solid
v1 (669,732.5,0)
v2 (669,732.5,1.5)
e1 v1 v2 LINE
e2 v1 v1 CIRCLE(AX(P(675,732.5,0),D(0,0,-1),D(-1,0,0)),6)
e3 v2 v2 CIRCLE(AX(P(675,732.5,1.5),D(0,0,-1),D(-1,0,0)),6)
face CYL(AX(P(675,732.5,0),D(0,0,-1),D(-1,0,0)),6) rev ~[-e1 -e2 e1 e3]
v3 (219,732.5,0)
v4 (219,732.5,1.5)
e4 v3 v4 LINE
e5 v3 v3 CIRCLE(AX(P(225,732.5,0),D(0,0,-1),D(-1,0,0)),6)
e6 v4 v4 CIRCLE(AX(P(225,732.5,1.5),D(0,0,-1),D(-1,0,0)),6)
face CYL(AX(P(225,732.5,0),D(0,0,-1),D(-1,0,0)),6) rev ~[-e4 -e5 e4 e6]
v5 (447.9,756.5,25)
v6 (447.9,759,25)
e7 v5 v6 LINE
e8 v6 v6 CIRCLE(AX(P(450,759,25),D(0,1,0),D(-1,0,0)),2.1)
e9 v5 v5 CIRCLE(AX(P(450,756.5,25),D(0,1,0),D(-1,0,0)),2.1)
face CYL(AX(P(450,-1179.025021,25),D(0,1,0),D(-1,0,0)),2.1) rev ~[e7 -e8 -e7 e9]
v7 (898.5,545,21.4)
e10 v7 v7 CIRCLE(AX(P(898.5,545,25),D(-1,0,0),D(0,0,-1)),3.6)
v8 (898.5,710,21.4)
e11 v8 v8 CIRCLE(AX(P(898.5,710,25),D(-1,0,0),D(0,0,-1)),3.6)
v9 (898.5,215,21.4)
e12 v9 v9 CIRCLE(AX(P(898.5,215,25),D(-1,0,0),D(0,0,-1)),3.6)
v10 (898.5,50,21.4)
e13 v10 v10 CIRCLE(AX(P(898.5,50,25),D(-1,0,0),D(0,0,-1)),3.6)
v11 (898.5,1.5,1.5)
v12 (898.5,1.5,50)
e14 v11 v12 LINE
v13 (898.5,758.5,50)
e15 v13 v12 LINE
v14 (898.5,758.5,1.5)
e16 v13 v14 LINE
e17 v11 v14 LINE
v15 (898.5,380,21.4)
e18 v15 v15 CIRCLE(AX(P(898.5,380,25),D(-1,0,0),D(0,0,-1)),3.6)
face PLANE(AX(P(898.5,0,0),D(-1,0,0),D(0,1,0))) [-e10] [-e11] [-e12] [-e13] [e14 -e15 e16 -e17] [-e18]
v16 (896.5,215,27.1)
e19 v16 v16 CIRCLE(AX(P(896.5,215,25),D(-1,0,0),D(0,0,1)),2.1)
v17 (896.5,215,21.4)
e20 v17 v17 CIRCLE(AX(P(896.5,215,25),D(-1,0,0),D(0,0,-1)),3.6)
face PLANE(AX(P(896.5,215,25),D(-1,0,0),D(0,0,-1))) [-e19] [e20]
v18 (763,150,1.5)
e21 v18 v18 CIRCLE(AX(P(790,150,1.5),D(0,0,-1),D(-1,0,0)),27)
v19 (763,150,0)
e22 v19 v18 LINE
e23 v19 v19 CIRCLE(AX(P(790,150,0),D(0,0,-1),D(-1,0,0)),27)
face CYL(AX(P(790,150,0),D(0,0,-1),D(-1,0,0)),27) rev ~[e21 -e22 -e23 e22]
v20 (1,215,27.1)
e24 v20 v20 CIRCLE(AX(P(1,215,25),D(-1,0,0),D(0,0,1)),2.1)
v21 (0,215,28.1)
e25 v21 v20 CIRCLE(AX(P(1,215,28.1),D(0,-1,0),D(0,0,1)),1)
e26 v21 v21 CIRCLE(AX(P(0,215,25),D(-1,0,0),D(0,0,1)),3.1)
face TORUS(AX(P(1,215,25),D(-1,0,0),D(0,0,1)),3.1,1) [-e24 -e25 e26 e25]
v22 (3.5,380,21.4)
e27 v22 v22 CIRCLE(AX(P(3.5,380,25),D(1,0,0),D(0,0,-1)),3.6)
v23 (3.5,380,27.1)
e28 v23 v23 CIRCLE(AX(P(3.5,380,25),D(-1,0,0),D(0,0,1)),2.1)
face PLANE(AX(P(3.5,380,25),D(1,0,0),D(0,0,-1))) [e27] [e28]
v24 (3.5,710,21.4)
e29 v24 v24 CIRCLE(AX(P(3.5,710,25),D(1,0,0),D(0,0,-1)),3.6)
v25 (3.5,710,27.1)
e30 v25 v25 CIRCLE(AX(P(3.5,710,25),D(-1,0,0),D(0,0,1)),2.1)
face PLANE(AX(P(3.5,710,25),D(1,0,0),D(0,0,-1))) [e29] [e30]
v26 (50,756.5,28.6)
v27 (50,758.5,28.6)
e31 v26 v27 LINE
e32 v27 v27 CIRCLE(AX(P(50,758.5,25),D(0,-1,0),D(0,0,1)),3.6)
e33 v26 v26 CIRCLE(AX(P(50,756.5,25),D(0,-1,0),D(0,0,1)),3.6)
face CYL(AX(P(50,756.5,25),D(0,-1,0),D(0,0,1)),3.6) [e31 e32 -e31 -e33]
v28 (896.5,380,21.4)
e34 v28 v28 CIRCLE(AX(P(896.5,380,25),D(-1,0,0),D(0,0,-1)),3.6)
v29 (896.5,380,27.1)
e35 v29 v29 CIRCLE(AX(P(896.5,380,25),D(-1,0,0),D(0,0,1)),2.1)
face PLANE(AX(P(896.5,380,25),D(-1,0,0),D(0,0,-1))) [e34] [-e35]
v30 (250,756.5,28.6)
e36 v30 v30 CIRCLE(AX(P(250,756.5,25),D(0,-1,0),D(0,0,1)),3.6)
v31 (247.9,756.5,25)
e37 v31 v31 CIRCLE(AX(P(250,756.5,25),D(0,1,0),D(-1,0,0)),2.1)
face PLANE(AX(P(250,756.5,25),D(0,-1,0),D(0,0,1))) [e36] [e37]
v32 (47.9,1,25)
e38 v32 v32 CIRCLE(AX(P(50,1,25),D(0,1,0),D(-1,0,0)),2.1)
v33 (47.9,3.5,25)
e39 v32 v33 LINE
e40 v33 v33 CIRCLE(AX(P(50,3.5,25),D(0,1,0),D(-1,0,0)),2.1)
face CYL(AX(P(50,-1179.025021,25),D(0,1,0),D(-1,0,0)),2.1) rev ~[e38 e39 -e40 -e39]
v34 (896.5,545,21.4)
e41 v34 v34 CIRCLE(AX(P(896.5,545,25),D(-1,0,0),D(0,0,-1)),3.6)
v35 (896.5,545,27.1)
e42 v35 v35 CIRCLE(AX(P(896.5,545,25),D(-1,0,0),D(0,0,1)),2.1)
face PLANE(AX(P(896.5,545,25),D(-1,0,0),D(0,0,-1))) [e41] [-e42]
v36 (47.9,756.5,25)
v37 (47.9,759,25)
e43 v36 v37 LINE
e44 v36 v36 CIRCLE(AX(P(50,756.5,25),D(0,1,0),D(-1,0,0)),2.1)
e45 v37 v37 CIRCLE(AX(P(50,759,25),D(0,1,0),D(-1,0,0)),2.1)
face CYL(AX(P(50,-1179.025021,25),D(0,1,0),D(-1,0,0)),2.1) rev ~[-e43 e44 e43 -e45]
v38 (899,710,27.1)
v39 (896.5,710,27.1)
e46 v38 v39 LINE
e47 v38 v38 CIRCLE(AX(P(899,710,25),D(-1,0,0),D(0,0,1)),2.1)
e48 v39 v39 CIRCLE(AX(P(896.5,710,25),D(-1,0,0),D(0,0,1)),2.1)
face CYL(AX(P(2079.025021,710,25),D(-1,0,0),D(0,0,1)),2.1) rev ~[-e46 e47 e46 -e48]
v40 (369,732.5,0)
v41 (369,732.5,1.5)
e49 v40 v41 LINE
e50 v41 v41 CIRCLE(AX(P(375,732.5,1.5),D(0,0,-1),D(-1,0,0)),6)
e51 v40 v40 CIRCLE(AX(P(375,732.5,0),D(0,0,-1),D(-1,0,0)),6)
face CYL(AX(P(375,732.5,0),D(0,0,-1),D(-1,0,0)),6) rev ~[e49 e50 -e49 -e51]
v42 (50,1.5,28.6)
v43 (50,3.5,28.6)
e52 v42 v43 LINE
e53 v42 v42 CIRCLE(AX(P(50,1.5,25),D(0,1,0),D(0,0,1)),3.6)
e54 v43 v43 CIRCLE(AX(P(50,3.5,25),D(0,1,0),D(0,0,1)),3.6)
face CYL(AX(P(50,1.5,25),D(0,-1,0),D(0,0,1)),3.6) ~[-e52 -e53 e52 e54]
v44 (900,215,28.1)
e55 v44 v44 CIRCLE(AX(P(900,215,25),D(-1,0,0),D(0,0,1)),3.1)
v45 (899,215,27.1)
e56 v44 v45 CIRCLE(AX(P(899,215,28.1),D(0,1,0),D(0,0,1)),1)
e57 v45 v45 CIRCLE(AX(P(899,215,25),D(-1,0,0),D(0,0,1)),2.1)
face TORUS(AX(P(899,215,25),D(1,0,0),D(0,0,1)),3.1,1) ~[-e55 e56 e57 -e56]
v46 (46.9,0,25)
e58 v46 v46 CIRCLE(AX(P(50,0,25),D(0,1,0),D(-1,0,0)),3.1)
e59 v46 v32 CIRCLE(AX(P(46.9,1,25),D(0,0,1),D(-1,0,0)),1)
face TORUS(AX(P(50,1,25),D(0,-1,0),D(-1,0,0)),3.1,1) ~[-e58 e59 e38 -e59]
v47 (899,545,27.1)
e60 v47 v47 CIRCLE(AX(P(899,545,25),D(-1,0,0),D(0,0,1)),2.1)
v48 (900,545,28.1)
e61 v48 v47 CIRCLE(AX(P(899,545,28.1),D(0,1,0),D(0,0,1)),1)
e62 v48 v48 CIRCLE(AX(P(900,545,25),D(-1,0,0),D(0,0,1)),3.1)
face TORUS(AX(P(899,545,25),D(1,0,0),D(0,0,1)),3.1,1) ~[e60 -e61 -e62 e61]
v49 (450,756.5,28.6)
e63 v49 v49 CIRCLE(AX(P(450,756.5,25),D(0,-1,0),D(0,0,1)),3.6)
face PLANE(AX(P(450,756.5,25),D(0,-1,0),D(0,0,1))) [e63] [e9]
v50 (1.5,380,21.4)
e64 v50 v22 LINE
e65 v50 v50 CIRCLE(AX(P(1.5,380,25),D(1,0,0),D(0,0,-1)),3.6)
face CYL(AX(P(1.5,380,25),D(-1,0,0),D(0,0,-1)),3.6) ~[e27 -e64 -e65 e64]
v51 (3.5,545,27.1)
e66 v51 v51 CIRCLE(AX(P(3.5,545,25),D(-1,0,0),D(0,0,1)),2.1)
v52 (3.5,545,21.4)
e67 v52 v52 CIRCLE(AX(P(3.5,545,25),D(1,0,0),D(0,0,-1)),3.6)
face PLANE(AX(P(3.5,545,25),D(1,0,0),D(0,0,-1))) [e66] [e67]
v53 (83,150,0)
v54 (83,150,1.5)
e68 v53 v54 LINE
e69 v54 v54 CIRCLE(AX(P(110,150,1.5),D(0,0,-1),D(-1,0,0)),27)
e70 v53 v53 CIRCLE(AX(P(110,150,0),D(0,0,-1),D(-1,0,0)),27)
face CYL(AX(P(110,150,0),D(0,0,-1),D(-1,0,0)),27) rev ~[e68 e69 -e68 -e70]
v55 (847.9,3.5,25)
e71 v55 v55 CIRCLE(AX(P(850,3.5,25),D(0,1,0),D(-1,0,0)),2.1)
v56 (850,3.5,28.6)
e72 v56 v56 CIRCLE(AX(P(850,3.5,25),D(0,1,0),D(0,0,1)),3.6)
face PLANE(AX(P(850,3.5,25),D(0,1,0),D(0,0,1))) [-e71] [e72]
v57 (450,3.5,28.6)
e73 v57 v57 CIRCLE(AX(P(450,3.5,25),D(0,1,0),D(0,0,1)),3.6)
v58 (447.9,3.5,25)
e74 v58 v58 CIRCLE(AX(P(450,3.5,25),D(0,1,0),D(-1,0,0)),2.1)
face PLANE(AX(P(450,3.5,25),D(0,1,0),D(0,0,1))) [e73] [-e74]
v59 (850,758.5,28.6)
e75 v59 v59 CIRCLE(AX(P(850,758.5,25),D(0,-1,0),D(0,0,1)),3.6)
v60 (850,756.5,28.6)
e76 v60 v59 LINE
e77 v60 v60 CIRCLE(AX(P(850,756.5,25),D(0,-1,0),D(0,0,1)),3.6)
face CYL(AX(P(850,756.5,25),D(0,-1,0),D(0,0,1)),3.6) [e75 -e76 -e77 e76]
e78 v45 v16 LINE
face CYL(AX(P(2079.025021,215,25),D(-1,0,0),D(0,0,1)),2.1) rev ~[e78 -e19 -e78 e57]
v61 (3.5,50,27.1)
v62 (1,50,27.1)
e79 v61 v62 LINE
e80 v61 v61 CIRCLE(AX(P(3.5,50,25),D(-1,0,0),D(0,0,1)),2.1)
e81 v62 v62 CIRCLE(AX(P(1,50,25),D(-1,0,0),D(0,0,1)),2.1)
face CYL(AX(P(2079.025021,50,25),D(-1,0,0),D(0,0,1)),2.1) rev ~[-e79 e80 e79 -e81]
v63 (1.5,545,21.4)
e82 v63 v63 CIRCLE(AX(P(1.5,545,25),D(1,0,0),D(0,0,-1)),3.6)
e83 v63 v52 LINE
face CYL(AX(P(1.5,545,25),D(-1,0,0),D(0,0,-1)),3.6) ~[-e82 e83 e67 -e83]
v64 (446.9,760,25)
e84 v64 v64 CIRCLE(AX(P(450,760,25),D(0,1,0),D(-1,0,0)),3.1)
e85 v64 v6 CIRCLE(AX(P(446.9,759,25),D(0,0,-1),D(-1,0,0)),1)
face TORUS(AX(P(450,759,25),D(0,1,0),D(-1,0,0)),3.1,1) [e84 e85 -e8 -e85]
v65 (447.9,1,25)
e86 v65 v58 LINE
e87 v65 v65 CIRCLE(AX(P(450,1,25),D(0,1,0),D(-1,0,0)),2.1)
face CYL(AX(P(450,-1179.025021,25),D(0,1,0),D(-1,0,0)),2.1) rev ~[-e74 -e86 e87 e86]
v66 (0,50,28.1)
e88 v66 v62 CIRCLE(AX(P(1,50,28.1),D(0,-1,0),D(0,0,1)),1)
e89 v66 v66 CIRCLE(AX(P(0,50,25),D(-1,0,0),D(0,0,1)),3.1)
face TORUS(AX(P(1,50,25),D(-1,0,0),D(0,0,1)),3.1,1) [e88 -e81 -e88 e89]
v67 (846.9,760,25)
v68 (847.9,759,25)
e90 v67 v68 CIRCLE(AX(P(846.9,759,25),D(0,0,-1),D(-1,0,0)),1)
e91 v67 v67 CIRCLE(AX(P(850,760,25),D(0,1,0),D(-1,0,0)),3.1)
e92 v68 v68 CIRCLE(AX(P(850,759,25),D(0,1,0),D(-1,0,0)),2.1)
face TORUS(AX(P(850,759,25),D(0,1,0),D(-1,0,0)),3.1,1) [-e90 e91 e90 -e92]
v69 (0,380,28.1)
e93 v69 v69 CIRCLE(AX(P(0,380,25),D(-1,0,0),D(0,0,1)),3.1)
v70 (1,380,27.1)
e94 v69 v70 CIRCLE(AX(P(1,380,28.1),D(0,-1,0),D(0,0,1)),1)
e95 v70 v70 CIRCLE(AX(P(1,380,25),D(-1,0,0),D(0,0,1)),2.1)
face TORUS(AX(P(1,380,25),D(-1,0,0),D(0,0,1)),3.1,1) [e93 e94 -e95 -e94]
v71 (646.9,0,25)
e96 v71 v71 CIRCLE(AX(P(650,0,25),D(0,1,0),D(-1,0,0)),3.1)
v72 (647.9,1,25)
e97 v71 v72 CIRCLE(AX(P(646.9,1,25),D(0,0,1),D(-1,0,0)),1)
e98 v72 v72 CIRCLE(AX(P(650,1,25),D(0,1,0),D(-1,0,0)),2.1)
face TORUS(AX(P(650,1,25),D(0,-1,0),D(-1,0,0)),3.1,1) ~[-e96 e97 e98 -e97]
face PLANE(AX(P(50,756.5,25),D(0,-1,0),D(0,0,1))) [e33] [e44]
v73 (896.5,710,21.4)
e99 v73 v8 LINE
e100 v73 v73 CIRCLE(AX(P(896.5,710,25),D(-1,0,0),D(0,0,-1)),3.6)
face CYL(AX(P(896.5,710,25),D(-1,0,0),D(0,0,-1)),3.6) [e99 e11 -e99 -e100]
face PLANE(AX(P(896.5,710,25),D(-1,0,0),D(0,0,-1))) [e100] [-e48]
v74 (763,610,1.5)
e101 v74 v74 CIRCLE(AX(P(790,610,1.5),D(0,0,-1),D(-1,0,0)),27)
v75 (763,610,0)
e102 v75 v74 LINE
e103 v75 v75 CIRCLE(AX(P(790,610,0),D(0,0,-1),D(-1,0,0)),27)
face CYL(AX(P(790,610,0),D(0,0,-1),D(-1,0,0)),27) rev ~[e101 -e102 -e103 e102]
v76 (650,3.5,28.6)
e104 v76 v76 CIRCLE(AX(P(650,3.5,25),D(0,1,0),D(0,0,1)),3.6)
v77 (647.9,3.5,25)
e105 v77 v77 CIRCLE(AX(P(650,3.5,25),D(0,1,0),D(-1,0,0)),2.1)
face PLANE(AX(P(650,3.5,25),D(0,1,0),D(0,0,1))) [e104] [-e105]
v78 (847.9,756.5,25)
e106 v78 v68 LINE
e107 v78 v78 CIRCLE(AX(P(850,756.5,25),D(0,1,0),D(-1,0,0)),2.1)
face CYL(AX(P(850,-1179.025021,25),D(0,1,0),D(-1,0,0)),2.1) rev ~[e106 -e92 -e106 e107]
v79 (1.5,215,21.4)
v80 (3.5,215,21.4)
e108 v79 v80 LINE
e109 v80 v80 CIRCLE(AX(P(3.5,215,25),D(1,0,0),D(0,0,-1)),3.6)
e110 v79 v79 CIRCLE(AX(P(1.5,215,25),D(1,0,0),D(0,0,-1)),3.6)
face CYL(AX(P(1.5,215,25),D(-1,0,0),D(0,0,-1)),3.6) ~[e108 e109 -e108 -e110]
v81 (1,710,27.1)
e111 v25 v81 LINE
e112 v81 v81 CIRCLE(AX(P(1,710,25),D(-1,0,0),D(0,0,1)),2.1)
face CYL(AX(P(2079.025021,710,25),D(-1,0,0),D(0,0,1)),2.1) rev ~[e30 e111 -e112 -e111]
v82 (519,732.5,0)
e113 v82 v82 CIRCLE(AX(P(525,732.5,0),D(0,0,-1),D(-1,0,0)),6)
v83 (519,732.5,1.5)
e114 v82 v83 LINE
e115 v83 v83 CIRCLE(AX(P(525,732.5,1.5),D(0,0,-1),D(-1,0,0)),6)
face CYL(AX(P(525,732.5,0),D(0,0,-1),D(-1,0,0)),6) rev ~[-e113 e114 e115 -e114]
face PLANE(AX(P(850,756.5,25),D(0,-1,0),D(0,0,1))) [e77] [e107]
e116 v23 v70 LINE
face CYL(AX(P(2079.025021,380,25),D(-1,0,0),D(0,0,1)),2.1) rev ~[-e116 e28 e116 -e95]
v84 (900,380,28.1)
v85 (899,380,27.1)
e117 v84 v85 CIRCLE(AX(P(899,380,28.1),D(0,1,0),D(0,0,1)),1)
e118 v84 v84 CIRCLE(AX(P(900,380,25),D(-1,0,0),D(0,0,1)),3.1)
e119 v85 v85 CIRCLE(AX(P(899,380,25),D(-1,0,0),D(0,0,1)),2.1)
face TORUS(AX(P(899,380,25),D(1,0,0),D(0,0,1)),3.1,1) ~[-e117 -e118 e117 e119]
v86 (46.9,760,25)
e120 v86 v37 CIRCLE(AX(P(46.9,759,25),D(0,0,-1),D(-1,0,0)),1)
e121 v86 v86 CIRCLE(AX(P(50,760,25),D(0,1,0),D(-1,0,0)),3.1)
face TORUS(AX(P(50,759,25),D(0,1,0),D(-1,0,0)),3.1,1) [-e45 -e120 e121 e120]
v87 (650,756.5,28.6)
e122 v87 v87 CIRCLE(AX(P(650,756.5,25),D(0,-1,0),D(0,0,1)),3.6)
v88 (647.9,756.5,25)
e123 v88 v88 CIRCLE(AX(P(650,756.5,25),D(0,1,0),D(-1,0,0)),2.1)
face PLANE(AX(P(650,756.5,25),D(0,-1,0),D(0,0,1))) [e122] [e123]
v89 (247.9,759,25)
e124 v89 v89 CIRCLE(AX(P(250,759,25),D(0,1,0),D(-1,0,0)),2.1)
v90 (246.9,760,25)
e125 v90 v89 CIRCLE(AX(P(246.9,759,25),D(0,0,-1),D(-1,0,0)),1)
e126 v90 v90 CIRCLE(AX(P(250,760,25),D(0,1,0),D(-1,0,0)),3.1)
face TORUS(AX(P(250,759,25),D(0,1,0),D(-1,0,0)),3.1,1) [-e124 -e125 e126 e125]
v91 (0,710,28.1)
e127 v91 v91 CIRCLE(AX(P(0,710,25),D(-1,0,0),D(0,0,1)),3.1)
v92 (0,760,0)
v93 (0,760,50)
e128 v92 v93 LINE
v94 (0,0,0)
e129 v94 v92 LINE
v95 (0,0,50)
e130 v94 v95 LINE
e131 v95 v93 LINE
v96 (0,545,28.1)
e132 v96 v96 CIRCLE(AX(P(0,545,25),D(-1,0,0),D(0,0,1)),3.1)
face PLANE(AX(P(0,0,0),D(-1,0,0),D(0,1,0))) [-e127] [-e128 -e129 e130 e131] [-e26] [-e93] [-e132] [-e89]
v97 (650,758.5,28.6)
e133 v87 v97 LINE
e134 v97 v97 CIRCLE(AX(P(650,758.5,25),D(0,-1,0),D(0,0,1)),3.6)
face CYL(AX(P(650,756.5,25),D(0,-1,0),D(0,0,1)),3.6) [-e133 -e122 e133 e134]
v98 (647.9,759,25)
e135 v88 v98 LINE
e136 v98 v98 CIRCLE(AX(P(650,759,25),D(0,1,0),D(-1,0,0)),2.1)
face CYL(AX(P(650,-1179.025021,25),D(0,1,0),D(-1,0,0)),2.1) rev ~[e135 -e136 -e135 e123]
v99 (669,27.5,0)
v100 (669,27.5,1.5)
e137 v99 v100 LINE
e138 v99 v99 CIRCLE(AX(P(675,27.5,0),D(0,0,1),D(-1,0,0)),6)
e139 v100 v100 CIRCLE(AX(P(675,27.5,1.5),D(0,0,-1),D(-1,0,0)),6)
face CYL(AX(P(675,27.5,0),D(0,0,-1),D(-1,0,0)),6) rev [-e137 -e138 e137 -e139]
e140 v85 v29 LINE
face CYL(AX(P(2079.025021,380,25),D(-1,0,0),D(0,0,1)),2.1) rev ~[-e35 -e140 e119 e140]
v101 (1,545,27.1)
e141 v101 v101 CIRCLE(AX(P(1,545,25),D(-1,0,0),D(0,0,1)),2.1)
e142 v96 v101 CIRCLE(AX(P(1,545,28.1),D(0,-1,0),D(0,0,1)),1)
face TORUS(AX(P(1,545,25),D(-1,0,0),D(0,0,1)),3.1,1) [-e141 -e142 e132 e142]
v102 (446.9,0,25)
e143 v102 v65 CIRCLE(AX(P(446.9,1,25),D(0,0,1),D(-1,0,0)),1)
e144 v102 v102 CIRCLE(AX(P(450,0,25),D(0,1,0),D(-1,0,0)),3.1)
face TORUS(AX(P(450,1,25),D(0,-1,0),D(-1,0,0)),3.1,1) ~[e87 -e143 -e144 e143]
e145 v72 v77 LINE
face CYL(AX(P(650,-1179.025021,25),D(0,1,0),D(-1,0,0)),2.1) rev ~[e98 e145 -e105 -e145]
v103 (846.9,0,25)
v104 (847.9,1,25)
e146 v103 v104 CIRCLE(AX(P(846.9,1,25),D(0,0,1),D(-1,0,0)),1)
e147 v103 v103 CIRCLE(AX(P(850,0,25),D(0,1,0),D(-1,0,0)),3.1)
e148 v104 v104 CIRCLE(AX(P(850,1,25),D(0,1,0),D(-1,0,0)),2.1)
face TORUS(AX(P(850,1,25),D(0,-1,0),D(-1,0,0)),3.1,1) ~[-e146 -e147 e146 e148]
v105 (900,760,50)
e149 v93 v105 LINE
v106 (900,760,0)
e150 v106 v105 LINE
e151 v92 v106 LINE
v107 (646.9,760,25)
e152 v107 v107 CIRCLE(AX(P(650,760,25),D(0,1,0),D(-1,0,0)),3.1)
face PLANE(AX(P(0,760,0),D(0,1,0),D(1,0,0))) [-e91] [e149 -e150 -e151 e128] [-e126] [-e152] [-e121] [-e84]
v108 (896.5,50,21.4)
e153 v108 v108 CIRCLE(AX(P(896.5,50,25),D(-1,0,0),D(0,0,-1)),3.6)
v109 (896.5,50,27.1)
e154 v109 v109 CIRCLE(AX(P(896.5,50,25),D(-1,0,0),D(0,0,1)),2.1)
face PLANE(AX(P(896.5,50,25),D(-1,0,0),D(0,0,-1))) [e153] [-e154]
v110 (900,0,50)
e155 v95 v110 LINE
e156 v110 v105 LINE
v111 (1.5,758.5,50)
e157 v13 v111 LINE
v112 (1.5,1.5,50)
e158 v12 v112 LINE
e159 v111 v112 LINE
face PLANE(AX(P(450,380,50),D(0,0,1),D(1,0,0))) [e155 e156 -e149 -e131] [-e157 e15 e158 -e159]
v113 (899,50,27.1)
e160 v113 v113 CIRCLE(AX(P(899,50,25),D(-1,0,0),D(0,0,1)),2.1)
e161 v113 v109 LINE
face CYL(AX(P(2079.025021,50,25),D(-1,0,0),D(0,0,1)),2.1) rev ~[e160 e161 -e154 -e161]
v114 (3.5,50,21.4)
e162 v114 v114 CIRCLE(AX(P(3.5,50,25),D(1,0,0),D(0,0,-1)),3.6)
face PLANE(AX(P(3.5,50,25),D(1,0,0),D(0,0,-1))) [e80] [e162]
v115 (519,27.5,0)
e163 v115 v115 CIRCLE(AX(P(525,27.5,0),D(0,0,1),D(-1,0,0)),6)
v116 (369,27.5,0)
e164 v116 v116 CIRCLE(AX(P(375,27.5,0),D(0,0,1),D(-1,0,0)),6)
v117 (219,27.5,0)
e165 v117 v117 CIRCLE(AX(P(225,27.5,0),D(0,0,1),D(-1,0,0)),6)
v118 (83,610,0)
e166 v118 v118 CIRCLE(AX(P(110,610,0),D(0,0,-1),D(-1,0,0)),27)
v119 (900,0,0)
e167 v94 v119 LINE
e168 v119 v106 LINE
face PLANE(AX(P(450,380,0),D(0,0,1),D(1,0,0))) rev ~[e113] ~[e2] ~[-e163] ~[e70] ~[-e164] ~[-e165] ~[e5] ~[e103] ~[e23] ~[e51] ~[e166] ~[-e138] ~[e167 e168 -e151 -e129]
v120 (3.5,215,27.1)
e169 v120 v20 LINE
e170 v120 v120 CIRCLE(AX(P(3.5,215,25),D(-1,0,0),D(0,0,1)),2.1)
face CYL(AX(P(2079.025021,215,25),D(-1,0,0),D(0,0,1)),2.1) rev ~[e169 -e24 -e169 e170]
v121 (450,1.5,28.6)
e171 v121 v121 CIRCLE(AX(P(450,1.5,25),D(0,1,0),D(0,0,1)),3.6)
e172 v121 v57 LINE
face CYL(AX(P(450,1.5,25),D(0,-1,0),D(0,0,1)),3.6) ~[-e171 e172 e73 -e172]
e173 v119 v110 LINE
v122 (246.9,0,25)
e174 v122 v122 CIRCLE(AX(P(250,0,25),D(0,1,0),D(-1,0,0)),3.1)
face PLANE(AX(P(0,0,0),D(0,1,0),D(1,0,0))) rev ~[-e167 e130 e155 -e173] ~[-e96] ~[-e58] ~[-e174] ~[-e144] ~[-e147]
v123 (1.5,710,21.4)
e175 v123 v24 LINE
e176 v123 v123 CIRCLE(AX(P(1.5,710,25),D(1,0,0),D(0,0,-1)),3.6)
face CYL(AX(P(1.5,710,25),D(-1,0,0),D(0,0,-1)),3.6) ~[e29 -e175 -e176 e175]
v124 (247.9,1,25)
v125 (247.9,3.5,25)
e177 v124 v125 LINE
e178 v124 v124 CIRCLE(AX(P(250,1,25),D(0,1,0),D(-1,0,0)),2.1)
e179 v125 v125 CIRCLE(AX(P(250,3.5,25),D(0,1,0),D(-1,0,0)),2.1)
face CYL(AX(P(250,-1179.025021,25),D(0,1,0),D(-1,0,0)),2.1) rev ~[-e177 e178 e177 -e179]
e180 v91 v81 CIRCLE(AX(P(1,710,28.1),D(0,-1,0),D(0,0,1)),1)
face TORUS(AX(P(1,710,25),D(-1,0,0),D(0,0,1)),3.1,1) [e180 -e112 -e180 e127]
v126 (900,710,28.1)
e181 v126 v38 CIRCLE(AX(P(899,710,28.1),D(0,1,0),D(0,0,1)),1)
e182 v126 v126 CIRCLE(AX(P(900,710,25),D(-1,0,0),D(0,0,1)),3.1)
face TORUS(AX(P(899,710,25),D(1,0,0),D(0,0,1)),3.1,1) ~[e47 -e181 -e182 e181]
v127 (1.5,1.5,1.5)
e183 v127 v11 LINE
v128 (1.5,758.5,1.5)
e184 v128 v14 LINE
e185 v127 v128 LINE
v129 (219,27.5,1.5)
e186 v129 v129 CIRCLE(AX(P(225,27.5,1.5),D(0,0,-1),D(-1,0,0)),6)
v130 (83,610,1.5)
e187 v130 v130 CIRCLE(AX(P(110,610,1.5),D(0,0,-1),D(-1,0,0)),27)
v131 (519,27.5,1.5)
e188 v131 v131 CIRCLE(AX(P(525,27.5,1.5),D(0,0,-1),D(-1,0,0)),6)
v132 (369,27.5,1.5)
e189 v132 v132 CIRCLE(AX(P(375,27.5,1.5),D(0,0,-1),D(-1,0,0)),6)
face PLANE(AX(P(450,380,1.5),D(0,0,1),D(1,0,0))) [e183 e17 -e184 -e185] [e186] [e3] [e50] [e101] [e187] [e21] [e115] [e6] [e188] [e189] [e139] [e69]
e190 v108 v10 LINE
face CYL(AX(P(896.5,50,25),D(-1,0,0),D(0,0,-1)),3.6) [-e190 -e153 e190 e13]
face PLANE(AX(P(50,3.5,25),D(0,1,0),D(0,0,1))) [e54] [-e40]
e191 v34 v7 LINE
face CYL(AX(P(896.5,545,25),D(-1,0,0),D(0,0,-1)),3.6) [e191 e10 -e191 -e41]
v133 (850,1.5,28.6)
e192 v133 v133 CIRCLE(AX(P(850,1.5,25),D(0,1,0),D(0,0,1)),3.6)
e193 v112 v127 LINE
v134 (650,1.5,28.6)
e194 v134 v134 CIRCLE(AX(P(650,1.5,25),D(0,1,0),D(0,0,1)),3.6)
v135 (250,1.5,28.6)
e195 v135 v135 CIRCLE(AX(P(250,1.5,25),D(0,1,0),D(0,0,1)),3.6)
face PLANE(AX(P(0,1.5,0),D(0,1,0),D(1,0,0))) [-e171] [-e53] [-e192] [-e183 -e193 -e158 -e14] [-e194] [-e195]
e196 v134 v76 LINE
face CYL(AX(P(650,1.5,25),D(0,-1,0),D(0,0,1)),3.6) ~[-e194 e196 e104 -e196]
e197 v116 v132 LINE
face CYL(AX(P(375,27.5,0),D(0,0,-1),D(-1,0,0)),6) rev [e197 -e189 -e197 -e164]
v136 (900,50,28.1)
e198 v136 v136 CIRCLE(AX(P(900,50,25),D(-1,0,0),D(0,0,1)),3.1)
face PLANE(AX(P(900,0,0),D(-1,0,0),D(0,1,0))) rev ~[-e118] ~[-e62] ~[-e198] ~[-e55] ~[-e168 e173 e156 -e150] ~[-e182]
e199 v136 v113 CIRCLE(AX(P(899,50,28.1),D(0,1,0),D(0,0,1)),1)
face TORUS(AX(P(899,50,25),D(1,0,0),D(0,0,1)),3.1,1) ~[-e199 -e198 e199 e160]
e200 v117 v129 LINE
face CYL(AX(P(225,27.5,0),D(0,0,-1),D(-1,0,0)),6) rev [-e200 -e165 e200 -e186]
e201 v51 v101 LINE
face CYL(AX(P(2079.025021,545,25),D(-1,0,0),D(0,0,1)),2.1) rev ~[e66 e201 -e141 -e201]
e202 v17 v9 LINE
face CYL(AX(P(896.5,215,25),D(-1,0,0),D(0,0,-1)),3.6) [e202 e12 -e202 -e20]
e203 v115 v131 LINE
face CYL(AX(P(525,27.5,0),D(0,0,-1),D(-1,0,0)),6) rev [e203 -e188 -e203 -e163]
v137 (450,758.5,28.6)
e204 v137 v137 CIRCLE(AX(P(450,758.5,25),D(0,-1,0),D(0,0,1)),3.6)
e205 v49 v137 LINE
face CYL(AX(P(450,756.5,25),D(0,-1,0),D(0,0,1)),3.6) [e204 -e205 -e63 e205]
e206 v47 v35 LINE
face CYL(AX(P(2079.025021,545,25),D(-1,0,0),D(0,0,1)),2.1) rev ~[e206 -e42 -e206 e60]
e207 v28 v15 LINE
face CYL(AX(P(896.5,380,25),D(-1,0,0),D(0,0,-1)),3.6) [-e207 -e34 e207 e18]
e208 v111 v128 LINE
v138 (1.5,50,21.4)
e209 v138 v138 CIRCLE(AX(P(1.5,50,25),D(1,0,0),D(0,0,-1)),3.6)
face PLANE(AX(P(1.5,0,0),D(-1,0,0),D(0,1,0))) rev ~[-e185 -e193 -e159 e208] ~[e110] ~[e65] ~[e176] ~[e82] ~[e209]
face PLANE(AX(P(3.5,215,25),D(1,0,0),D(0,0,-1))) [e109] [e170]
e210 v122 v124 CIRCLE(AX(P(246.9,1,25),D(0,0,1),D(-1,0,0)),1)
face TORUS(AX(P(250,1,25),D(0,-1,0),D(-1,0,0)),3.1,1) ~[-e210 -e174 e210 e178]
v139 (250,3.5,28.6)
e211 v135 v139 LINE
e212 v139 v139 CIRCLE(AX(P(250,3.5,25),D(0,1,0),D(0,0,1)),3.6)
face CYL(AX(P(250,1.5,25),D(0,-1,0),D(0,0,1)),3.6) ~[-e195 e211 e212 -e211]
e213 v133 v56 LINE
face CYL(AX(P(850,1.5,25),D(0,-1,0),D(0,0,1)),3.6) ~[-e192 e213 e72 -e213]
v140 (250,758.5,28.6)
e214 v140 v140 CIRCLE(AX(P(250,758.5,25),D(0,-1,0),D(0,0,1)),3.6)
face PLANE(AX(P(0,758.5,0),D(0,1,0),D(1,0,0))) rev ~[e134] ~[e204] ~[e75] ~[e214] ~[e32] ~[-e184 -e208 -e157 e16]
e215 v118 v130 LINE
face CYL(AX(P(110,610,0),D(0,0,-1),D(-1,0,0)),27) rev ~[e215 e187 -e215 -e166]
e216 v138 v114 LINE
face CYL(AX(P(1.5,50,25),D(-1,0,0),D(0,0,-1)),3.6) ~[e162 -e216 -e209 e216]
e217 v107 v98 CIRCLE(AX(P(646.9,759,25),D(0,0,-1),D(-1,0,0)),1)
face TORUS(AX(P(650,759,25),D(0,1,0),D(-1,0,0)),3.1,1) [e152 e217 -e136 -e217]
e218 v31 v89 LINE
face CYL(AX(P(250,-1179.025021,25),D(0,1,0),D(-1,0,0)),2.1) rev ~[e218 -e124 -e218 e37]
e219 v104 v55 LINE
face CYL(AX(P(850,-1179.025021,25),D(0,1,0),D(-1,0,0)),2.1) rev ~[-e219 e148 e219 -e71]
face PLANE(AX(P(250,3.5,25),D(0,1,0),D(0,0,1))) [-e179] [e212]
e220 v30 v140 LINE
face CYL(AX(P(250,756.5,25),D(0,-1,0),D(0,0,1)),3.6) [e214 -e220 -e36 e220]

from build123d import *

# Parameters (mm, degrees)
SKETCH_1_W          = 900
SKETCH_1_H          = 760
EXTRUDE_1_DEPTH     = 50
SHELL_1_T           = -1.5
SKETCH_2_R          = 27
CUT_EXTRUDE_1_DEPTH = 1180.025020939
SKETCH_3_R          = 6
CUT_EXTRUDE_3_DEPTH = 1180.025020939
SKETCH_6_R          = 3.6
EXTRUDE_1_2_DEPTH   = 2
EXTRUDE_START       = 2
SKETCH_7_R          = 3.6
EXTRUDE_2_DEPTH     = 2
HOLE_WIZARD_M5_1_D  = 4.2
SKETCH_10_R         = 3.6
EXTRUDE_3_DEPTH     = 2
SKETCH_11_R         = 3.6
EXTRUDE_4_DEPTH     = 2
HOLE_WIZARD_M5_2_D  = 4.2
FILLET_1_R          = 1


with BuildPart() as part:
    # 草图1 → Extrude 1 (new body)
    with BuildSketch(Plane.XY):
        with Locations((450, 380)):
            Rectangle(SKETCH_1_W, SKETCH_1_H)
    extrude(amount=EXTRUDE_1_DEPTH)

    # 抽壳1
    shell_1_openings = [part.faces().sort_by_distance(p)[0] for p in [
        (450, 380, 50),
    ]]
    offset(amount=SHELL_1_T, openings=shell_1_openings, kind=Kind.INTERSECTION)

    # 草图2 → 切除-拉伸1 (cut, through all)
    with BuildSketch(Plane(origin=(0, 0, 0), x_dir=(-1, 0, 0), z_dir=(0, 0, -1))):
        with Locations((-790, 610)):
            Circle(SKETCH_2_R)
        with Locations((-110, 610)):
            Circle(SKETCH_2_R)
        with Locations((-790, 150)):
            Circle(SKETCH_2_R)
        with Locations((-110, 150)):
            Circle(SKETCH_2_R)
    extrude(amount=-CUT_EXTRUDE_1_DEPTH, mode=Mode.SUBTRACT)

    # 草图3 → 切除-拉伸3 (cut, through all)
    with BuildSketch(Plane(origin=(0, 0, 0), x_dir=(-1, 0, 0), z_dir=(0, 0, -1))):
        with Locations((-675, 732.5)):
            Circle(SKETCH_3_R)
        with Locations((-525, 732.5)):
            Circle(SKETCH_3_R)
        with Locations((-375, 732.5)):
            Circle(SKETCH_3_R)
        with Locations((-225, 732.5)):
            Circle(SKETCH_3_R)
    cut_extrude_3 = extrude(amount=-CUT_EXTRUDE_3_DEPTH, mode=Mode.SUBTRACT)

    # 镜向1: 切除-拉伸3 across plane
    add(cut_extrude_3.mirror(Plane.ZX.offset(380)), mode=Mode.SUBTRACT)

    # 草图6 → Extrude 1 2 (add)
    with BuildSketch(Plane(origin=(0, 1.5, 0), x_dir=(1, 0, 0), z_dir=(0, 1, 0))):
        with Locations(Location((50, -25, 0), (0, 0, 270))):
            Circle(SKETCH_6_R)
        with Locations(Location((250, -25, 0), (0, 0, 270))):
            Circle(SKETCH_6_R)
        with Locations(Location((450, -25, 0), (0, 0, 270))):
            Circle(SKETCH_6_R)
        with Locations(Location((650, -25, 0), (0, 0, 270))):
            Circle(SKETCH_6_R)
        with Locations(Location((850, -25, 0), (0, 0, 270))):
            Circle(SKETCH_6_R)
    extrude(amount=EXTRUDE_1_2_DEPTH)

    # 草图7 → 凸台-拉伸2 (add)
    with BuildSketch(Plane.XZ.offset(-758.5).offset(EXTRUDE_START)):
        with Locations(Location((50, 25, 0), (0, 0, 90))):
            Circle(SKETCH_7_R)
        with Locations(Location((250, 25, 0), (0, 0, 90))):
            Circle(SKETCH_7_R)
        with Locations(Location((450, 25, 0), (0, 0, 90))):
            Circle(SKETCH_7_R)
        with Locations(Location((650, 25, 0), (0, 0, 90))):
            Circle(SKETCH_7_R)
        with Locations(Location((850, 25, 0), (0, 0, 90))):
            Circle(SKETCH_7_R)
    extrude(amount=-EXTRUDE_2_DEPTH)

    # M5 螺纹孔1 (through all)
    with Locations(Plane.XZ):
        with Locations((50, 25), (250, 25), (450, 25), (650, 25), (850, 25)):
            Hole(HOLE_WIZARD_M5_1_D / 2)

    # 草图10 → 凸台-拉伸3 (add)
    with BuildSketch(Plane(origin=(1.5, 0, 0), x_dir=(0, 0, -1), z_dir=(1, 0, 0))):
        with Locations((-25, 710)):
            Circle(SKETCH_10_R)
        with Locations((-25, 545)):
            Circle(SKETCH_10_R)
        with Locations((-25, 380)):
            Circle(SKETCH_10_R)
        with Locations((-25, 215)):
            Circle(SKETCH_10_R)
        with Locations((-25, 50)):
            Circle(SKETCH_10_R)
    extrude(amount=EXTRUDE_3_DEPTH)

    # 草图11 → 凸台-拉伸4 (add)
    with BuildSketch(Plane.ZY.offset(-898.5).offset(EXTRUDE_START)):
        with Locations(Location((25, 710, 0), (0, 0, 180))):
            Circle(SKETCH_11_R)
        with Locations(Location((25, 545, 0), (0, 0, 180))):
            Circle(SKETCH_11_R)
        with Locations(Location((25, 380, 0), (0, 0, 180))):
            Circle(SKETCH_11_R)
        with Locations(Location((25, 215, 0), (0, 0, 180))):
            Circle(SKETCH_11_R)
        with Locations(Location((25, 50, 0), (0, 0, 180))):
            Circle(SKETCH_11_R)
    extrude(amount=-EXTRUDE_4_DEPTH)

    # M5 螺纹孔2 (through all)
    with Locations(Plane(origin=(900, 0, 0), x_dir=(0, 0, -1), z_dir=(1, 0, 0))):
        with Locations((-25, 710), (-25, 545), (-25, 380), (-25, 215), (-25, 50)):
            Hole(HOLE_WIZARD_M5_2_D / 2)

    # 圆角1
    fillet_1_edges = [part.edges().sort_by_distance(p)[0] for p in [
        (852.1, 760, 25),
        (852.1, 0, 25),
        (652.1, 0, 25),
        (652.1, 760, 25),
        (452.1, 0, 25),
        (452.1, 760, 25),
        (252.1, 0, 25),
        (252.1, 760, 25),
        (52.1, 0, 25),
        (52.1, 760, 25),
        (0, 50, 22.9),
        (900, 50, 22.9),
        (0, 215, 22.9),
        (900, 215, 22.9),
        (0, 380, 22.9),
        (900, 380, 22.9),
        (0, 545, 22.9),
        (900, 545, 22.9),
        (0, 710, 22.9),
        (900, 710, 22.9),
    ]]
    fillet(fillet_1_edges, radius=FILLET_1_R)


solid = part.part
